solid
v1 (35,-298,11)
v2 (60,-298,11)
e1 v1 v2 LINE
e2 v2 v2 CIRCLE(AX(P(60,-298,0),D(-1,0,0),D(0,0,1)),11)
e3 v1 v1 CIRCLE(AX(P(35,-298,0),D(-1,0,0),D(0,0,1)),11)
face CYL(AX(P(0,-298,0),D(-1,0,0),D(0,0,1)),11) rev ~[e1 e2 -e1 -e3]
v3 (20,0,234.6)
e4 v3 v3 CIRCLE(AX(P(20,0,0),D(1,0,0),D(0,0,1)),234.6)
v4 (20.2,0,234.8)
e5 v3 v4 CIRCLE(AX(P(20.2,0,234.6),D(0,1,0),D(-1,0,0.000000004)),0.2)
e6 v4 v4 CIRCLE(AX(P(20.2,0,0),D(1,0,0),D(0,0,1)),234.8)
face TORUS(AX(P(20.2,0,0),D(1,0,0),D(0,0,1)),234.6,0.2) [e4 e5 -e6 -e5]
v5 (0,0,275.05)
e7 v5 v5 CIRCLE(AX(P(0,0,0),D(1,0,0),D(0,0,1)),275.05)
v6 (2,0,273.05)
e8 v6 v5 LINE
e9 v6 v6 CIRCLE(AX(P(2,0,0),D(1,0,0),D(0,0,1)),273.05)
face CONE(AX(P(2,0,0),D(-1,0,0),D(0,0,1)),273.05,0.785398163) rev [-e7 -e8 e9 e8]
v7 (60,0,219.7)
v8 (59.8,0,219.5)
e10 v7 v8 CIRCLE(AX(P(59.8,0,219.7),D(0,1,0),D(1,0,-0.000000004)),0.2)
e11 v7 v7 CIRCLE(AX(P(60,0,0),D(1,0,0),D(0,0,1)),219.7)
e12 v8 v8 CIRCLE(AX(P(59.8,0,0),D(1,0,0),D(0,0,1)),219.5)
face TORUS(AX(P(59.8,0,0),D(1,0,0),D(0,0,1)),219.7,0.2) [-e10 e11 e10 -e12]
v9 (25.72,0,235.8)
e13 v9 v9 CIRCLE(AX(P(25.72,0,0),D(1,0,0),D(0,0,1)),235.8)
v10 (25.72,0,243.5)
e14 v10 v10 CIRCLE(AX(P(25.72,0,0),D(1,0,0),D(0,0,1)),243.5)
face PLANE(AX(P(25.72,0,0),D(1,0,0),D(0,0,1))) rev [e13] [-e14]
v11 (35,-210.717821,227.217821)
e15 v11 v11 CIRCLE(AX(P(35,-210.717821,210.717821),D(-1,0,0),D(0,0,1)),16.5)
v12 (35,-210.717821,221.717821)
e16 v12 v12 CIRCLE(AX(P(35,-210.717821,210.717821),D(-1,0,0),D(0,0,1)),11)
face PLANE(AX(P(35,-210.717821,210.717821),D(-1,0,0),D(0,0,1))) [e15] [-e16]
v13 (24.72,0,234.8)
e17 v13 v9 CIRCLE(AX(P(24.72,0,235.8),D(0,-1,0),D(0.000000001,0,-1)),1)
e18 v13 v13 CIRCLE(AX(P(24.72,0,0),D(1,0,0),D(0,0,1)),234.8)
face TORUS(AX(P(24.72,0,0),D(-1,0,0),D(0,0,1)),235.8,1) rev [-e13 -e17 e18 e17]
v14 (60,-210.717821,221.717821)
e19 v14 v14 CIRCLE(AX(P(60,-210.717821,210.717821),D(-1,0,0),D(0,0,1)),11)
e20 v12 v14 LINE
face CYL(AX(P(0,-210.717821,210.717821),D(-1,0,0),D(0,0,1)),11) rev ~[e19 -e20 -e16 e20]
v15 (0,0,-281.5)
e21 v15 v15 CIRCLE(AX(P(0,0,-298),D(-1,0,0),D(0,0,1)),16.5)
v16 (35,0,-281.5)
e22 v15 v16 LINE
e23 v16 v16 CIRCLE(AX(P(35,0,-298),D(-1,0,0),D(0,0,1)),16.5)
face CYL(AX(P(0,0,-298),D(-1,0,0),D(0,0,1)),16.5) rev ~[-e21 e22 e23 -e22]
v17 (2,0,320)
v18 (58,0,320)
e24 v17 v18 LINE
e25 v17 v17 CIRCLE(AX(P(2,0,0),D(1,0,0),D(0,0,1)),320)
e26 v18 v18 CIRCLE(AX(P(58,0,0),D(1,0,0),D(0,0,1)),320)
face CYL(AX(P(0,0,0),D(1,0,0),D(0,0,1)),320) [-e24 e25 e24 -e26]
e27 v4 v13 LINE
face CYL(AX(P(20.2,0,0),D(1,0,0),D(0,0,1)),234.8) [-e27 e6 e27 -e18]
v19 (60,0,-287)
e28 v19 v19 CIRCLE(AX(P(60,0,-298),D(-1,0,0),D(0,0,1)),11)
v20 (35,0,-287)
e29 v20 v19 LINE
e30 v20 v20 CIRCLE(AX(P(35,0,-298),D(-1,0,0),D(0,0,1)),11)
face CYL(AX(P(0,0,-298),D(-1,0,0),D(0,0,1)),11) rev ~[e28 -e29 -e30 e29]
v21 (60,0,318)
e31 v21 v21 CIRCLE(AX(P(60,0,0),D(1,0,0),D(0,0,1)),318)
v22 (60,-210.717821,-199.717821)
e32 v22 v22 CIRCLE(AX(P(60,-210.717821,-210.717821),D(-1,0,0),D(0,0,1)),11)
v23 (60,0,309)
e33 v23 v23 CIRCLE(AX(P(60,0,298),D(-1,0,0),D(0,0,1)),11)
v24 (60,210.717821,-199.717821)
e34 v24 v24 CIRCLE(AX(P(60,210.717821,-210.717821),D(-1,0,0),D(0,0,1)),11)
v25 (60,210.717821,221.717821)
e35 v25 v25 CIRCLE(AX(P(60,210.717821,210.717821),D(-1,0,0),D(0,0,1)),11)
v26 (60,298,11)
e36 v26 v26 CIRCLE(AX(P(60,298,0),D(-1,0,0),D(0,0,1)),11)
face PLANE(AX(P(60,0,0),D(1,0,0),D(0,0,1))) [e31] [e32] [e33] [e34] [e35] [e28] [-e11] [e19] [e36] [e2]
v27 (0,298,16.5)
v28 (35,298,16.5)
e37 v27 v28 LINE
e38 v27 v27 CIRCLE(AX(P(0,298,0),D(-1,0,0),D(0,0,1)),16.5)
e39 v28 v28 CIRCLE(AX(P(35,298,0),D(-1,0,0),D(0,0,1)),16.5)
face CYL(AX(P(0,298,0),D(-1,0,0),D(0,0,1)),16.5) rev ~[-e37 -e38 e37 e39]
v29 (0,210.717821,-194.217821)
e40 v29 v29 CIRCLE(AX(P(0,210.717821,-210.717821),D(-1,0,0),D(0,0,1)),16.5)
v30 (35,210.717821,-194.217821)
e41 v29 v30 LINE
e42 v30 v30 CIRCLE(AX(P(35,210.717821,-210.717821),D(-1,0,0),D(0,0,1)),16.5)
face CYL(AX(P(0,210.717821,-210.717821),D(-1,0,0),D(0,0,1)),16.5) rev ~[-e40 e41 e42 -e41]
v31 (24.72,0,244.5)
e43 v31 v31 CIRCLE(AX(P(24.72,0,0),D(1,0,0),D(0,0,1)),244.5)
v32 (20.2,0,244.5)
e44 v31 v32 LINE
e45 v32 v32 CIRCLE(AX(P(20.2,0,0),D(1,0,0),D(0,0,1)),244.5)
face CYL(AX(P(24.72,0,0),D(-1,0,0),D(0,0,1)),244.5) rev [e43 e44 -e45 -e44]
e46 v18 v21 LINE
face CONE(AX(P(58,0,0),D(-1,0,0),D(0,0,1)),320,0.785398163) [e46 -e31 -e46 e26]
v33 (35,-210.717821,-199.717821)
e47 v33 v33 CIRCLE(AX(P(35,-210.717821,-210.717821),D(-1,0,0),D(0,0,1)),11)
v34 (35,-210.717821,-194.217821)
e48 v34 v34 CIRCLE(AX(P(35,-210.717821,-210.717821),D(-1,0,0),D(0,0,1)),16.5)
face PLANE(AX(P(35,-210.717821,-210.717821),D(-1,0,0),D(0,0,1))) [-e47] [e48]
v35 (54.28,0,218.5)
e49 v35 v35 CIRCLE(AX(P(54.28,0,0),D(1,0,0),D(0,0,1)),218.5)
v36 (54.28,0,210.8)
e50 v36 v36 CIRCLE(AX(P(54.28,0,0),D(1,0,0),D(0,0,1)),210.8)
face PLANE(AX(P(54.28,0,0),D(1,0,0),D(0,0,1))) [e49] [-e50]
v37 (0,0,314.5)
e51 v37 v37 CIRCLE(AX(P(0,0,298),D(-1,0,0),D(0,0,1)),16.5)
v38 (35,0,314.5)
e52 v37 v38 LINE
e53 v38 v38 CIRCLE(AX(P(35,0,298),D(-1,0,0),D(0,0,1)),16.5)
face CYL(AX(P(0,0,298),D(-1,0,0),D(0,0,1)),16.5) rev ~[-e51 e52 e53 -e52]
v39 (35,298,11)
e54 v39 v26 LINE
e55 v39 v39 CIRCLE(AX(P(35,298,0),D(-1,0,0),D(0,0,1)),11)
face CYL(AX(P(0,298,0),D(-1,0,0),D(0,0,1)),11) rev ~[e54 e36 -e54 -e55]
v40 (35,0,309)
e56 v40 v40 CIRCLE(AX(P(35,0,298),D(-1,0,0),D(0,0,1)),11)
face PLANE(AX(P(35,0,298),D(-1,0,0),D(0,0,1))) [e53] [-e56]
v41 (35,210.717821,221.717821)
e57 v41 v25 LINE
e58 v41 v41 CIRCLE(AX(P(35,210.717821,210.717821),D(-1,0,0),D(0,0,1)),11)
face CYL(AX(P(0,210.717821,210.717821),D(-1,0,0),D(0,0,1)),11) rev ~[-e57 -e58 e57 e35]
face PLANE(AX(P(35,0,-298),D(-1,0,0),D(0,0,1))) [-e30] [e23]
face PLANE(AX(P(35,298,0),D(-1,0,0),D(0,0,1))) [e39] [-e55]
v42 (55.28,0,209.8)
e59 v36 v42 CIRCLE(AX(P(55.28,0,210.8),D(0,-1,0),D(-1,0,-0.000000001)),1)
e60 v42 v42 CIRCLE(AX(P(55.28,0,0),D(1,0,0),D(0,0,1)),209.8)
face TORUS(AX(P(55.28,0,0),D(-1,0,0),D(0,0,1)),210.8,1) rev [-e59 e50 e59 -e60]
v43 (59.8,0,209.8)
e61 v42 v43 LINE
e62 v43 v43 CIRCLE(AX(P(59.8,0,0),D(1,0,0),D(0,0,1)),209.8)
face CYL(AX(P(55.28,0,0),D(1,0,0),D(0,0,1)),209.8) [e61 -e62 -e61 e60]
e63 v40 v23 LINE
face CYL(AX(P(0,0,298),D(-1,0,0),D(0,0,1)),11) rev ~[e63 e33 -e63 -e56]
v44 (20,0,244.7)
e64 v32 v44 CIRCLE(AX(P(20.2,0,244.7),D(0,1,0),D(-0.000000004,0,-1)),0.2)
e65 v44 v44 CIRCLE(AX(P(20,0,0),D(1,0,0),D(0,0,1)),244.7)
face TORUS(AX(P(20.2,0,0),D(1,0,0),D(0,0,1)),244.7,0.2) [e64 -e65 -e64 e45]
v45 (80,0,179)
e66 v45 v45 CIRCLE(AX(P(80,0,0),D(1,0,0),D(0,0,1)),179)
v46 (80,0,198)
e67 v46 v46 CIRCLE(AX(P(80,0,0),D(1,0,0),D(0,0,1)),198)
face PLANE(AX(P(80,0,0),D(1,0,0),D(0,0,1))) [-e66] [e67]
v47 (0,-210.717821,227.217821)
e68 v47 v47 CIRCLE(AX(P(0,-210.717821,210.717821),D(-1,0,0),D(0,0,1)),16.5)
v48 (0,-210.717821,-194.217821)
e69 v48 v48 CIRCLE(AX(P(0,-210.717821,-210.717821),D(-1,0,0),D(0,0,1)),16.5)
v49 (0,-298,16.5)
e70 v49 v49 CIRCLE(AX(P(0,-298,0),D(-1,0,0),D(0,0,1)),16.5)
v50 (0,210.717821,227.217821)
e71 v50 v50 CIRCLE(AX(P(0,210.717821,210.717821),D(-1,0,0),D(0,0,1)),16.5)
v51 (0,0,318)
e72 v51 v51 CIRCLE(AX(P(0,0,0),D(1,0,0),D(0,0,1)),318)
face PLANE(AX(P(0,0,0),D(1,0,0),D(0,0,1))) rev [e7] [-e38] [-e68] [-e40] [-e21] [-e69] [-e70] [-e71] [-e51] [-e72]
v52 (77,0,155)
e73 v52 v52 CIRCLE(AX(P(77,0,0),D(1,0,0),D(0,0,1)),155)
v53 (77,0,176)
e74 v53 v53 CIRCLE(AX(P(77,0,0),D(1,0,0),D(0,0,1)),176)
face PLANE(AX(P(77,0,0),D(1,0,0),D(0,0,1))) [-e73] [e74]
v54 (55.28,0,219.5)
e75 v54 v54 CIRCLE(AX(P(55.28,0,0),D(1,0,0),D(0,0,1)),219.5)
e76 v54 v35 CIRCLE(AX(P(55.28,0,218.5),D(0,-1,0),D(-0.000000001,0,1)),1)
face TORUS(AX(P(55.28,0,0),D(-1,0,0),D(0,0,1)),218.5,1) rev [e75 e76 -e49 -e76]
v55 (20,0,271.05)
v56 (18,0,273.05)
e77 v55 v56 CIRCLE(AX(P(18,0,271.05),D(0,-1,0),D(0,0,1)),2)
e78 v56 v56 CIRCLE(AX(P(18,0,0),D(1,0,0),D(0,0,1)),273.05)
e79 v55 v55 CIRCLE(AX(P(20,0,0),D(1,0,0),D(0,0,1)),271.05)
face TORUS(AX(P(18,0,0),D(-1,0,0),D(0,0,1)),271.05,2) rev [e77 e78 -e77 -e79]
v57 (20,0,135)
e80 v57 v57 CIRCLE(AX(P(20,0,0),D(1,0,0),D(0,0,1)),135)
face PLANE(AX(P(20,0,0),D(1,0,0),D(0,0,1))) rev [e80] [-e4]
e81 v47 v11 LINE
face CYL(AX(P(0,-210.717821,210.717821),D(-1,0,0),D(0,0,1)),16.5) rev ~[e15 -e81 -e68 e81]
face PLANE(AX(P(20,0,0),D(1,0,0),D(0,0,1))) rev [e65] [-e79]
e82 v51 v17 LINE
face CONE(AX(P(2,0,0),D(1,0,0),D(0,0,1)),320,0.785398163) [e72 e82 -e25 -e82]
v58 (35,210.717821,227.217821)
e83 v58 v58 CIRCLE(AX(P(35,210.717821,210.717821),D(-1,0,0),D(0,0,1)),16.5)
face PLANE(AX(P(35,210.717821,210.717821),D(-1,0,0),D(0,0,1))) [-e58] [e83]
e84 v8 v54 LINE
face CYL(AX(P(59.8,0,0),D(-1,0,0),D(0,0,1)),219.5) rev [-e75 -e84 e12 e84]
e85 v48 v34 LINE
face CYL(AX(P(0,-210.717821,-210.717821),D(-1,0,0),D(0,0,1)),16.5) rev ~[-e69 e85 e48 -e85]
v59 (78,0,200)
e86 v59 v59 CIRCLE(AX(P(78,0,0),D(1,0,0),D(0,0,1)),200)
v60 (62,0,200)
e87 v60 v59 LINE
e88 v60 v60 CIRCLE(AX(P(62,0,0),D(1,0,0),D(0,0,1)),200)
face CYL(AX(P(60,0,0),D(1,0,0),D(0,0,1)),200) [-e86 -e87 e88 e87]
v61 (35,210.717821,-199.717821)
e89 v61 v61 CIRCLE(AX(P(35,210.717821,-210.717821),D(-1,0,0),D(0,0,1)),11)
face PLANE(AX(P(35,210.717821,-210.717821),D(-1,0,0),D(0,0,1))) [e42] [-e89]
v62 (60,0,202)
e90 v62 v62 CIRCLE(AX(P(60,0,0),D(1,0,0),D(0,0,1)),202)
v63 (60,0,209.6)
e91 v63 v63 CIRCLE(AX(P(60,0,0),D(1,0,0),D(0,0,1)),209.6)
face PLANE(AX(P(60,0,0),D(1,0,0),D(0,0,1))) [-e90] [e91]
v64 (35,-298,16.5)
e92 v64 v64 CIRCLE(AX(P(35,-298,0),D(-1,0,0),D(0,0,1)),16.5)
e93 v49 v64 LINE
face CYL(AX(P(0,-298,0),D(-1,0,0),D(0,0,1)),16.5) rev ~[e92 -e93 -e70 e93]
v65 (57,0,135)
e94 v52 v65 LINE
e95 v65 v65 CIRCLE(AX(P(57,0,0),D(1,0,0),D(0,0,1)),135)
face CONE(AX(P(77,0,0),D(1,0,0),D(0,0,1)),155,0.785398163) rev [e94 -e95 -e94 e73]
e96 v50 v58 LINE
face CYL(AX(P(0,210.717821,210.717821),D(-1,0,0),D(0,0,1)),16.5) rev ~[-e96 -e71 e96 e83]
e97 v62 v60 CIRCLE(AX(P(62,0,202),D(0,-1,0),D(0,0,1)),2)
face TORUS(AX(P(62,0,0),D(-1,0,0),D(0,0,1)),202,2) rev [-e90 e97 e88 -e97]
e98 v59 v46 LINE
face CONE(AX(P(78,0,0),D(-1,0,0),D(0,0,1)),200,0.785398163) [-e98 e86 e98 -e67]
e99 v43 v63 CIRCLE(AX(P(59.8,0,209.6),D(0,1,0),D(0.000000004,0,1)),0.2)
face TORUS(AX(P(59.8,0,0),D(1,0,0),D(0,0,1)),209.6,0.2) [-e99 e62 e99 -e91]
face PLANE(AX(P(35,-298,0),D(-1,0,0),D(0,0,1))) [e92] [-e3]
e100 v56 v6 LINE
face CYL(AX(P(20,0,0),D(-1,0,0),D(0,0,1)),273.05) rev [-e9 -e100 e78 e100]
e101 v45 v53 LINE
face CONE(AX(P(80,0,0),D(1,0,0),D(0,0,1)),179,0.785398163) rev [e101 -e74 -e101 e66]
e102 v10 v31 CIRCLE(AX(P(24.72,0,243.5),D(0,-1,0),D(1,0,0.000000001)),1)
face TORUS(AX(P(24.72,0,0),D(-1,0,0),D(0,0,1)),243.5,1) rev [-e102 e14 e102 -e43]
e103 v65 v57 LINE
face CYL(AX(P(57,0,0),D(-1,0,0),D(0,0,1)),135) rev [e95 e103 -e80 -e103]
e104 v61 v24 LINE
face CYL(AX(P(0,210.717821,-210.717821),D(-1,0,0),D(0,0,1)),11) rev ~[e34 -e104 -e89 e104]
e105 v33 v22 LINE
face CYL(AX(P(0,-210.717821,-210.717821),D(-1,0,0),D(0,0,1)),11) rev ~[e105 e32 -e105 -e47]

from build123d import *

# Parameters (mm, degrees)
FILLET1_R          = 2
CHAMFER1_SIZE      = 2
FILLET2_R          = 2
CHAMFER2_SIZE      = 2
SKETCH2_R          = 11
CUT_EXTRUDE1_DEPTH = 460.565011723
SKETCH3_R          = 16.5
CUT_EXTRUDE2_DEPTH = 35


with BuildPart() as part:
    # Sketch1 → Revolve1 (revolve)
    with BuildSketch(Plane.XY, mode=Mode.PRIVATE) as revolve1_sk:
        with BuildLine():
            Line((0, 273.05), (0, 320))
            Line((0, 320), (60, 320))
            Line((60, 320), (60, 219.7))
            ThreePointArc((60, 219.7), (59.941421356, 219.558578644), (59.8, 219.5))
            Line((59.8, 219.5), (55.28, 219.5))
            ThreePointArc((55.28, 219.5), (54.572893219, 219.207106781), (54.28, 218.5))
            Line((54.28, 218.5), (54.28, 210.8))
            ThreePointArc((54.28, 210.8), (54.572893219, 210.092893219), (55.28, 209.8))
            Line((55.28, 209.8), (59.8, 209.8))
            ThreePointArc((59.8, 209.8), (59.941421356, 209.741421356), (60, 209.6))
            Line((60, 209.6), (60, 200))
            Line((60, 200), (80, 200))
            Line((80, 200), (80, 179))
            Line((80, 179), (77, 176))
            Line((77, 176), (77, 155))
            Line((77, 155), (57, 135))
            Line((57, 135), (20, 135))
            Line((20, 135), (20, 234.6))
            ThreePointArc((20, 234.6), (20.058578644, 234.741421356), (20.2, 234.8))
            Line((20.2, 234.8), (24.72, 234.8))
            ThreePointArc((24.72, 234.8), (25.427106781, 235.092893219), (25.72, 235.8))
            Line((25.72, 235.8), (25.72, 243.5))
            ThreePointArc((25.72, 243.5), (25.427106781, 244.207106781), (24.72, 244.5))
            Line((24.72, 244.5), (20.2, 244.5))
            ThreePointArc((20.2, 244.5), (20.058578644, 244.558578644), (20, 244.7))
            Line((20, 244.7), (20, 273.05))
            Line((20, 273.05), (0, 273.05))
        make_face()
    revolve(revolve1_sk.sketch.rotate(Axis((0, 0, 0), (1, 0, 0)), 90), axis=Axis((0, 0, 0), (1, 0, 0)))

    # Fillet1
    fillet1_edges = [part.edges().sort_by_distance(p)[0] for p in [
        (20, 0, -273.05),
    ]]
    fillet(fillet1_edges, radius=FILLET1_R)

    # Chamfer1
    chamfer1_edges = [part.edges().sort_by_distance(p)[0] for p in [
        (0, 0, -273.05),
        (0, 0, -320),
        (60, 0, -320),
    ]]
    chamfer(chamfer1_edges, length=CHAMFER1_SIZE)

    # Fillet2
    fillet2_edges = [part.edges().sort_by_distance(p)[0] for p in [
        (60, 0, -200),
    ]]
    fillet(fillet2_edges, radius=FILLET2_R)

    # Chamfer2
    chamfer2_edges = [part.edges().sort_by_distance(p)[0] for p in [
        (80, 0, -200),
    ]]
    chamfer(chamfer2_edges, length=CHAMFER2_SIZE)

    # Sketch2 → Cut-Extrude1 (cut, through all)
    with BuildSketch(Plane.ZY):
        with Locations((0, 298)):
            Circle(SKETCH2_R)
        with Locations((210.717820794, 210.717820794)):
            Circle(SKETCH2_R)
        with Locations((298, 0)):
            Circle(SKETCH2_R)
        with Locations((210.717820794, -210.717820794)):
            Circle(SKETCH2_R)
        with Locations((0, -298)):
            Circle(SKETCH2_R)
        with Locations((-210.717820794, -210.717820794)):
            Circle(SKETCH2_R)
        with Locations((-298, 0)):
            Circle(SKETCH2_R)
        with Locations((-210.717820794, 210.717820794)):
            Circle(SKETCH2_R)
    extrude(amount=-CUT_EXTRUDE1_DEPTH, mode=Mode.SUBTRACT)

    # Sketch3 → Cut-Extrude2 (cut)
    with BuildSketch(Plane.ZY):
        with Locations((0, 298)):
            Circle(SKETCH3_R)
        with Locations((210.717820794, 210.717820794)):
            Circle(SKETCH3_R)
        with Locations((298, 0)):
            Circle(SKETCH3_R)
        with Locations((210.717820794, -210.717820794)):
            Circle(SKETCH3_R)
        with Locations((0, -298)):
            Circle(SKETCH3_R)
        with Locations((-210.717820794, -210.717820794)):
            Circle(SKETCH3_R)
        with Locations((-298, 0)):
            Circle(SKETCH3_R)
        with Locations((-210.717820794, 210.717820794)):
            Circle(SKETCH3_R)
    extrude(amount=-CUT_EXTRUDE2_DEPTH, mode=Mode.SUBTRACT)


solid = part.part
